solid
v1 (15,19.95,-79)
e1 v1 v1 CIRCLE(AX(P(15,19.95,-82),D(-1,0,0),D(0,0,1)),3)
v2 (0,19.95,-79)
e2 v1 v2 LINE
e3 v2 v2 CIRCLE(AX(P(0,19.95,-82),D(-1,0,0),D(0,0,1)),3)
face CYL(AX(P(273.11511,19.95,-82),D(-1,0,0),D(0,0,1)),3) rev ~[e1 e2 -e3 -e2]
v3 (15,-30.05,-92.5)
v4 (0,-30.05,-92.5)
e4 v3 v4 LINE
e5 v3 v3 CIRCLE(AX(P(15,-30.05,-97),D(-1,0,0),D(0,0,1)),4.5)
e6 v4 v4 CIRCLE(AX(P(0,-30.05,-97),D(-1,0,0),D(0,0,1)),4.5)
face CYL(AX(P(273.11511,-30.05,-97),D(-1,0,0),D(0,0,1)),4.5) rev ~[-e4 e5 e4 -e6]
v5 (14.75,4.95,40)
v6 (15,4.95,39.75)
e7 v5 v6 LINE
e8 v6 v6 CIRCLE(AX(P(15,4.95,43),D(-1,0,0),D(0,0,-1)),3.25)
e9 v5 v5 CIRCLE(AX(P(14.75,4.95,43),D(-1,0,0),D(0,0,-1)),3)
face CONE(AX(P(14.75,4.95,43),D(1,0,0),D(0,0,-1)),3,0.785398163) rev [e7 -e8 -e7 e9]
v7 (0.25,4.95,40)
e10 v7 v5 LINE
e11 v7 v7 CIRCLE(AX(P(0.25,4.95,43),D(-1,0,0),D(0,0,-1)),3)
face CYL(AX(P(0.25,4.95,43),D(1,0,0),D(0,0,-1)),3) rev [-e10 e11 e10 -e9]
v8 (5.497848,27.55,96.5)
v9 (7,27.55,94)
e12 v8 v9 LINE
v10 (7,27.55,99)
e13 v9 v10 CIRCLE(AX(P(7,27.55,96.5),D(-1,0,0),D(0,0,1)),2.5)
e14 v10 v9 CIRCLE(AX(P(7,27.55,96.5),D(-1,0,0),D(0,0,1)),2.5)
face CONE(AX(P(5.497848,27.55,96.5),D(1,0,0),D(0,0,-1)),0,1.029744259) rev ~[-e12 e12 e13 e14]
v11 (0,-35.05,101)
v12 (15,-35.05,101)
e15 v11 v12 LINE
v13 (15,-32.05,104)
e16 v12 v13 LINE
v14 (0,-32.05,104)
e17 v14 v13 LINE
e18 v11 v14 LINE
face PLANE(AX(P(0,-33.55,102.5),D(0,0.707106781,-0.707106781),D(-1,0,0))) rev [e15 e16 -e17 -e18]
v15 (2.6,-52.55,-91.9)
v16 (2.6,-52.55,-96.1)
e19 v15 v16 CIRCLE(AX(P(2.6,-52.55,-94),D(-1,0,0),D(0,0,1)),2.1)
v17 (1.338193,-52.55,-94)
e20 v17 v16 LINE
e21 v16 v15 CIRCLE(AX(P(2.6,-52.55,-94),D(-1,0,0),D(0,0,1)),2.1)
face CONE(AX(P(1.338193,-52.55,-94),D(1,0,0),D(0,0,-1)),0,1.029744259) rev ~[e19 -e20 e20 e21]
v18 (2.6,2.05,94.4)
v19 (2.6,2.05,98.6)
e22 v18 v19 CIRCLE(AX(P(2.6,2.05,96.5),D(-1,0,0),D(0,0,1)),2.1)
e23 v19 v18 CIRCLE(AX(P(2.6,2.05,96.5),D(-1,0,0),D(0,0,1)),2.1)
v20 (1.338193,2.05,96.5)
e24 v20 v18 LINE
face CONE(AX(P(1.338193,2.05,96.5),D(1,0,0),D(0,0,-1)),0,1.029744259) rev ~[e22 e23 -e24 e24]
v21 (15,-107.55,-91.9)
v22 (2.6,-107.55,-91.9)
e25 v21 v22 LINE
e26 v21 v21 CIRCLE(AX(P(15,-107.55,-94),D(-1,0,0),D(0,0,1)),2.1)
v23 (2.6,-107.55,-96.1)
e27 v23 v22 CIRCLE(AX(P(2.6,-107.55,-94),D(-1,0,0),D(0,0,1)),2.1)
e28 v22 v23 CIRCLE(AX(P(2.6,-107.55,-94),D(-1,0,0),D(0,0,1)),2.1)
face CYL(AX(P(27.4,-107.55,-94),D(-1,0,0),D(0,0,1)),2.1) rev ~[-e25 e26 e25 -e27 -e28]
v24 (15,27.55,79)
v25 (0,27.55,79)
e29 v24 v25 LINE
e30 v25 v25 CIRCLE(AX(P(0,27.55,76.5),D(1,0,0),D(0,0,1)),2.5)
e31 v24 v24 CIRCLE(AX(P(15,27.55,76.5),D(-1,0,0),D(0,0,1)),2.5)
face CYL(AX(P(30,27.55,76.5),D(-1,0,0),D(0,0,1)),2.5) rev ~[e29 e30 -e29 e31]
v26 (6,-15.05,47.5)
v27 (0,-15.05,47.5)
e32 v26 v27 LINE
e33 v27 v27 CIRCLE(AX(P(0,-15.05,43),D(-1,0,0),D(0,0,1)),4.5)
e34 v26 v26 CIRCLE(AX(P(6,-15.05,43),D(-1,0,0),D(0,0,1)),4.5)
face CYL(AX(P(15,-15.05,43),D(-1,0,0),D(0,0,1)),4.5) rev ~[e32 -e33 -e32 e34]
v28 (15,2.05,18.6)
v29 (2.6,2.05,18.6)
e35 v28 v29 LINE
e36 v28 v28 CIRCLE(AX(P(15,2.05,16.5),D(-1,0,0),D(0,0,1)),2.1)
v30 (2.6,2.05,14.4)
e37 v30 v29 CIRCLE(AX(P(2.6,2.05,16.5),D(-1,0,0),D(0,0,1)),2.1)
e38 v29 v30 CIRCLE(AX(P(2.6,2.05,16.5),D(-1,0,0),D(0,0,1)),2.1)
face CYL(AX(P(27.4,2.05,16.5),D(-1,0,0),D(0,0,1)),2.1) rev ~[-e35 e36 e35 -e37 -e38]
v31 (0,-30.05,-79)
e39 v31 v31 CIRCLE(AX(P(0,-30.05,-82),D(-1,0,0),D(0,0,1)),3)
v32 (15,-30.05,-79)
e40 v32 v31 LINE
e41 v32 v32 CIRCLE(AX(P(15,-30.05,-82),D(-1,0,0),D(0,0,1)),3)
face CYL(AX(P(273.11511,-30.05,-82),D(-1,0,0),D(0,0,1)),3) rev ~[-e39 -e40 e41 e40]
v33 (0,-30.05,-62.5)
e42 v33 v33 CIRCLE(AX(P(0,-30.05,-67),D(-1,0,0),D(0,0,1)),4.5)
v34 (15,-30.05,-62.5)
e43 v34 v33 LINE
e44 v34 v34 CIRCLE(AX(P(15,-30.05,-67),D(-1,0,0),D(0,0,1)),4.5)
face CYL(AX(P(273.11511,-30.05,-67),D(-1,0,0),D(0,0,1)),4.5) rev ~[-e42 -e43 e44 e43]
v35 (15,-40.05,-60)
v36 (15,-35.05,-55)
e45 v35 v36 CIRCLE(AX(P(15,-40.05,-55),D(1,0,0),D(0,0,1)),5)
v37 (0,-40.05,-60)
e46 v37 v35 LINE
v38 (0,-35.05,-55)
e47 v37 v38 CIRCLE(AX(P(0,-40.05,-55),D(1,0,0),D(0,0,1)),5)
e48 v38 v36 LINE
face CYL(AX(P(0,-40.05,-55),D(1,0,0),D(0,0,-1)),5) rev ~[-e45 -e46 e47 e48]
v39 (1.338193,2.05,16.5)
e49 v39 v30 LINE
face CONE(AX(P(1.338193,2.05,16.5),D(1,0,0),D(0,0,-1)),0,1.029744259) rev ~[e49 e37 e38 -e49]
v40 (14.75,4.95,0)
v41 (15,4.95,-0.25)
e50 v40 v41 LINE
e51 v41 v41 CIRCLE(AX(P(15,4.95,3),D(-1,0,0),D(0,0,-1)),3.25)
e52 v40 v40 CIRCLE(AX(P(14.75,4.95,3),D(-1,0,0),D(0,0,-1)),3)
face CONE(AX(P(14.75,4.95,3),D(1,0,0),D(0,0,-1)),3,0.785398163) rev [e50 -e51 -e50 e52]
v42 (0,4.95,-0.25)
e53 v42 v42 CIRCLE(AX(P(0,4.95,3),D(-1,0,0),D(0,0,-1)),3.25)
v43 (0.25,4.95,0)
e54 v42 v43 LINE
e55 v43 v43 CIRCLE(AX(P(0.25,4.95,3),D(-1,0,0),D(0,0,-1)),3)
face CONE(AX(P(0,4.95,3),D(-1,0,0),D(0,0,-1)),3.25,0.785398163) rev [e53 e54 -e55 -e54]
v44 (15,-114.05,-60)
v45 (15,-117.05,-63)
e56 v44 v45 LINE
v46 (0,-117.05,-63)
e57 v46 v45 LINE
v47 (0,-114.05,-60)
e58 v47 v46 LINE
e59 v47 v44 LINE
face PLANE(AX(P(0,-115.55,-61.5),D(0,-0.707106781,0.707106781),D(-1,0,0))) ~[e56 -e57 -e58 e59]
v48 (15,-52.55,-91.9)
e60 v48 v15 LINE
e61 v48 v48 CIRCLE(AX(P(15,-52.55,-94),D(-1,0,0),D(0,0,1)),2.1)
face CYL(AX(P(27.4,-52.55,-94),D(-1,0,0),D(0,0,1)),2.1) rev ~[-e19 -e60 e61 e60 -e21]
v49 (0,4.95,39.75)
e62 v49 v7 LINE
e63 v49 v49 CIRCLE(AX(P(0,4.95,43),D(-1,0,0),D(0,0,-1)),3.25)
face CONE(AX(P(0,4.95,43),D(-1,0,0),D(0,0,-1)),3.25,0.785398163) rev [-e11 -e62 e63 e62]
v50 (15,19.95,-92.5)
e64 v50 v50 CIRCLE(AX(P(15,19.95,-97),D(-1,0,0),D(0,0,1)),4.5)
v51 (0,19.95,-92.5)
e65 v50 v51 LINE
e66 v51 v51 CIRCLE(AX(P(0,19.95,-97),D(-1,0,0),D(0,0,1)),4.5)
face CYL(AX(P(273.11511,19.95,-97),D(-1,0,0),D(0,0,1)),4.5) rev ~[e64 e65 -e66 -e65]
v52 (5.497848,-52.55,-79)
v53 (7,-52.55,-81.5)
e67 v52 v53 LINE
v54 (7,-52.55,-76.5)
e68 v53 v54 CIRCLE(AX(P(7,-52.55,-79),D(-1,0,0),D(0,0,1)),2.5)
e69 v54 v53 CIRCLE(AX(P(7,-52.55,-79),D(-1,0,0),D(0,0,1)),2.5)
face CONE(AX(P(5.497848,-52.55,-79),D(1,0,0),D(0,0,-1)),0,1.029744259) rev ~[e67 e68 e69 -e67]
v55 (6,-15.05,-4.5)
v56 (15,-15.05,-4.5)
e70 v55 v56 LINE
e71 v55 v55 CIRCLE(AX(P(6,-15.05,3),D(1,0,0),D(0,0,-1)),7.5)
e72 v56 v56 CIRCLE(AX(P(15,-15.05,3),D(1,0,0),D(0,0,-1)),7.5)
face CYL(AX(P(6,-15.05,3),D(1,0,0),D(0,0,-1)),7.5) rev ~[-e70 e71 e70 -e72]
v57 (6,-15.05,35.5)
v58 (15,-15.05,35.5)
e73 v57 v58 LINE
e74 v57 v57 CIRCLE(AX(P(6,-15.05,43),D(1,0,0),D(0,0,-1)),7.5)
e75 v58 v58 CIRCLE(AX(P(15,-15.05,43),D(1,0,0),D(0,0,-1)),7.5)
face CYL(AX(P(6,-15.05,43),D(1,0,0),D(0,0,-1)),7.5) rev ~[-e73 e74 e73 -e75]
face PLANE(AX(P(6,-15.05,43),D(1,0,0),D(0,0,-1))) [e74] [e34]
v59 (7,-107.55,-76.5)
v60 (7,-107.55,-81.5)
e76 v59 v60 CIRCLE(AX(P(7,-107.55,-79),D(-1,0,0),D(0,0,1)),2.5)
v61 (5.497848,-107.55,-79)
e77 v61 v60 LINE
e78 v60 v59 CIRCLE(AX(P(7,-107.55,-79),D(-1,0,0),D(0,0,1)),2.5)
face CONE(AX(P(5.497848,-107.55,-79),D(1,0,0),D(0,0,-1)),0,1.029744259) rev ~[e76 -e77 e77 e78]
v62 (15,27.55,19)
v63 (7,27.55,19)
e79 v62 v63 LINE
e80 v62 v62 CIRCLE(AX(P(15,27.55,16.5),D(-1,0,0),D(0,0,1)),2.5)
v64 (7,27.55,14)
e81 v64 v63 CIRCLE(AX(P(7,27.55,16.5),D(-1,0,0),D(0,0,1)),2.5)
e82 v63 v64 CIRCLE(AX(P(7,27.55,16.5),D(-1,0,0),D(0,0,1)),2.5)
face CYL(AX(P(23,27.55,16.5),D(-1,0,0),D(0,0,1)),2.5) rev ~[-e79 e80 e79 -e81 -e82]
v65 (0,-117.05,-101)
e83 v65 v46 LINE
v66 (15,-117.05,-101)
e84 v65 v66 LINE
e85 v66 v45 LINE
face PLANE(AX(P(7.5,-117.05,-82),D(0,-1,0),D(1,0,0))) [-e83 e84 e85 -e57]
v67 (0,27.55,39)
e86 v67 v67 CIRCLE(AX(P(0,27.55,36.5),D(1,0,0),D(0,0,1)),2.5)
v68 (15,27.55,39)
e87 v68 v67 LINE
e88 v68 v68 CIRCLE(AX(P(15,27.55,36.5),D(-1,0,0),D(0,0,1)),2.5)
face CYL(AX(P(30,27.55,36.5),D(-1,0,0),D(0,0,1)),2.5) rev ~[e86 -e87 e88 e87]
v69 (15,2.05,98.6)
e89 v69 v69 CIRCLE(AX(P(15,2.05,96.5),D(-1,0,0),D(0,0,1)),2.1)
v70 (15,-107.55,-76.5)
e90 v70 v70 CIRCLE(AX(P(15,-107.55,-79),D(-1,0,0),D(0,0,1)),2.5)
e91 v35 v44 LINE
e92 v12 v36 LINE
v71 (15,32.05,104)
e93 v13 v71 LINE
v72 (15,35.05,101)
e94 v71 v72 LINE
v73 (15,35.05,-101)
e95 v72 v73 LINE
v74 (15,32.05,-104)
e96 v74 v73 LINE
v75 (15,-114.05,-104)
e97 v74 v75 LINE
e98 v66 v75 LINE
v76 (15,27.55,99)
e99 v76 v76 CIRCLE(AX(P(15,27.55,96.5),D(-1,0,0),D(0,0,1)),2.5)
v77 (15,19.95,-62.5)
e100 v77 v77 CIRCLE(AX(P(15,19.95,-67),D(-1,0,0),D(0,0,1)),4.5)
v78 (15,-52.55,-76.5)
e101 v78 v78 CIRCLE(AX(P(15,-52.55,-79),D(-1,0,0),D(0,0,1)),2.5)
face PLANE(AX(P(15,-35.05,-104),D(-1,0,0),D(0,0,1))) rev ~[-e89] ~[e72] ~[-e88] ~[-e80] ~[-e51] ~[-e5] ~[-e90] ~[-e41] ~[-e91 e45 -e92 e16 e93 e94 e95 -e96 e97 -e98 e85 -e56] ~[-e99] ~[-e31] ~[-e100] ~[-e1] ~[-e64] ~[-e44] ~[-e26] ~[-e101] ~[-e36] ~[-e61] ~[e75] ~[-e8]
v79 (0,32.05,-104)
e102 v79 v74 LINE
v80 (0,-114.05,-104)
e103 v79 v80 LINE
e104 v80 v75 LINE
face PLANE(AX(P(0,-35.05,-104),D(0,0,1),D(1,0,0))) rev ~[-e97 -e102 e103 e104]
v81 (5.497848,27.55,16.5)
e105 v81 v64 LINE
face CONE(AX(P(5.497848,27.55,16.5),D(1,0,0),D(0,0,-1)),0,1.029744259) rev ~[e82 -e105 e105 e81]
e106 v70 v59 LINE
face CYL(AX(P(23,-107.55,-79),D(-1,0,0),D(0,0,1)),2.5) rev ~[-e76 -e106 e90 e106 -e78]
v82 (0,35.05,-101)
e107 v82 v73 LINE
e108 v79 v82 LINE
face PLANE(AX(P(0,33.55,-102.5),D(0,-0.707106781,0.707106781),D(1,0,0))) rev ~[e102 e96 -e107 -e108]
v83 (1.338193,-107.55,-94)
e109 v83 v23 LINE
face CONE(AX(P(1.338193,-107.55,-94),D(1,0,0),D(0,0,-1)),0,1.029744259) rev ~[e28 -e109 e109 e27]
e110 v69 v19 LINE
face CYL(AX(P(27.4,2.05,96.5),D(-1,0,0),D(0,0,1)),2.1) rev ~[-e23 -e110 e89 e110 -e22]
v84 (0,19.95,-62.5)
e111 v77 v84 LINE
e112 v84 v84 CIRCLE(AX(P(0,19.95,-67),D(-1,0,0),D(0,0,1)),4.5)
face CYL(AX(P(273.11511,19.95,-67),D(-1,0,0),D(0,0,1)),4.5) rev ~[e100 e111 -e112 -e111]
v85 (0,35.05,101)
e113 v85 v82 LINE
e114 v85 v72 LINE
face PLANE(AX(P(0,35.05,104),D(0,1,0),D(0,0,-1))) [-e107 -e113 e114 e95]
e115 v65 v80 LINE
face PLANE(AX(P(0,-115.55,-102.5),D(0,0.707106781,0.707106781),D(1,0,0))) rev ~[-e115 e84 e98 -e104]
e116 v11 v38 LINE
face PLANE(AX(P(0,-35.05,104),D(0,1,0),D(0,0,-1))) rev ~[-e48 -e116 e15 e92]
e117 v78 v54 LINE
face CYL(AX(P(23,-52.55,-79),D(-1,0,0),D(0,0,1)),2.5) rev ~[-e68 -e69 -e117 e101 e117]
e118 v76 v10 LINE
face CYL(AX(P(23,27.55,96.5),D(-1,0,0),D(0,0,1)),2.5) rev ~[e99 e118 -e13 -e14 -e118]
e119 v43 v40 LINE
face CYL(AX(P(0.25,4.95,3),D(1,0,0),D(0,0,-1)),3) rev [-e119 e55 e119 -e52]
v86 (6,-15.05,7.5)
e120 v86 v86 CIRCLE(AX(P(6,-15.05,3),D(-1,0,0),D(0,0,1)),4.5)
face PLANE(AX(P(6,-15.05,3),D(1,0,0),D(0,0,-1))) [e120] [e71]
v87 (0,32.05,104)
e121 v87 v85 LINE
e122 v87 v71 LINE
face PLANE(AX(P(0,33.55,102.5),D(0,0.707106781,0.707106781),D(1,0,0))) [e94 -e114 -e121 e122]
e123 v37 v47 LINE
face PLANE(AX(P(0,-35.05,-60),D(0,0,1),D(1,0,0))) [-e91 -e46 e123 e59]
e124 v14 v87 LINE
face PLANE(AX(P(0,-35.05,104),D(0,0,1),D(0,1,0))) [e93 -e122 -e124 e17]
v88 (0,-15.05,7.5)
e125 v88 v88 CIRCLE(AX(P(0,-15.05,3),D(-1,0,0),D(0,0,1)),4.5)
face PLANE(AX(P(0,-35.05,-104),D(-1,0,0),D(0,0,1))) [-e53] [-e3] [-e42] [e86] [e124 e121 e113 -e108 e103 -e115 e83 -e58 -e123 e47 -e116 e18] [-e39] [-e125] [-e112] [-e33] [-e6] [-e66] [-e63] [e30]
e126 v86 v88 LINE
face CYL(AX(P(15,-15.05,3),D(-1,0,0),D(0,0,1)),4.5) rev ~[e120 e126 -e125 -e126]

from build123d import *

# Parameters (mm, degrees)
SKETCH1_W                                            = 208
SKETCH1_H                                            = 70.1
BOSS_EXTRUDE1_DEPTH                                  = 15
CBORE_FOR_M8_HEXAGON_SOCKET_HEAD_CAP_SCR_D           = 9
CBORE_FOR_M8_HEXAGON_SOCKET_HEAD_CAP_SCR_CBORE_D     = 15
CBORE_FOR_M8_HEXAGON_SOCKET_HEAD_CAP_SCR_CBORE_DEPTH = 9
F_6_0MM_BLIND_HOLE_1_AT_2_COUNT                      = 2
F_6_0MM_BLIND_HOLE_1_AT_2_PITCH                      = 40
SKETCH6_W                                            = 15
SKETCH6_H                                            = 44
BOSS_EXTRUDE2_DEPTH                                  = 82
M5_TAPPED_HOLE1_D                                    = 4.2
M5_TAPPED_HOLE1_DEPTH                                = 12.4
M5_TAPPED_HOLE1_TIP                                  = 1.2618073
F_5_0MM_BLIND_HOLE_1_D                               = 5
F_5_0MM_BLIND_HOLE_1_DEPTH                           = 8
F_5_0MM_BLIND_HOLE_1_TIP                             = 1.502151548
M6_TAPPED_HOLE1_D                                    = 5
M6_TAPPED_HOLE1_DEPTH                                = 15
M6_TAPPED_HOLE1_TIP                                  = 1.502151548
F_5_0MM_BLIND_HOLE_2_D                               = 5
F_5_0MM_BLIND_HOLE_2_DEPTH                           = 8
F_5_0MM_BLIND_HOLE_2_TIP                             = 1.502151548
M5_TAPPED_HOLE2_D                                    = 4.2
M5_TAPPED_HOLE2_DEPTH                                = 12.4
M5_TAPPED_HOLE2_TIP                                  = 1.2618073
M8_CLEARANCE_HOLE1_D                                 = 9
F_6_0MM_BLIND_HOLE_2_D                               = 6
FILLET1_R                                            = 5
CHAMFER1_SIZE                                        = 3


with BuildPart() as part:
    # Sketch1 → Boss-Extrude1 (new body)
    with BuildSketch(Plane(origin=(0, 0, 0), x_dir=(0, 0, -1), z_dir=(1, 0, 0))):
        Rectangle(SKETCH1_W, SKETCH1_H)
    extrude(amount=BOSS_EXTRUDE1_DEPTH)

    # CBORE for M8 Hexagon socket head cap screws1 (through all)
    with Locations(Plane(origin=(15, 0, 0), x_dir=(0, 0, -1), z_dir=(1, 0, 0))):
        with Locations((-43, -15.05), (-3, -15.05)):
            CounterBoreHole(CBORE_FOR_M8_HEXAGON_SOCKET_HEAD_CAP_SCR_D / 2, CBORE_FOR_M8_HEXAGON_SOCKET_HEAD_CAP_SCR_CBORE_D / 2, CBORE_FOR_M8_HEXAGON_SOCKET_HEAD_CAP_SCR_CBORE_DEPTH)

    # Sketch5 → Ø6.0mm blind hole 1 (revolve, cut)
    with BuildSketch(Plane(origin=(15, 4.95, 43), x_dir=(0, 0, -1), z_dir=(0, 1, 0))):
        Polygon((0, 0), (0, 15), (3.25, 15), (3, 14.75), (3, 0.25), (3.25, 0), align=None)
    f_6_0mm_blind_hole_1 = revolve(axis=Axis((21.35, 4.95, 43), (-1, 0, 0)), mode=Mode.SUBTRACT)

    # Ø6.0mm blind hole 1 at 2: Ø6.0mm blind hole 1 ×2
    with Locations(*[(0, 0, -i * F_6_0MM_BLIND_HOLE_1_AT_2_PITCH) for i in range(1, F_6_0MM_BLIND_HOLE_1_AT_2_COUNT)]):
        add(f_6_0mm_blind_hole_1, mode=Mode.SUBTRACT)

    # Sketch6 → Boss-Extrude2 (add)
    with BuildSketch(Plane.XZ.offset(35.05)):
        with Locations((7.5, -82)):
            Rectangle(SKETCH6_W, SKETCH6_H)
    extrude(amount=BOSS_EXTRUDE2_DEPTH)

    # M5 Tapped Hole1
    with Locations(Plane(origin=(15, 0, 0), x_dir=(0, 0, -1), z_dir=(1, 0, 0))):
        with Locations((94, -107.55), (94, -52.55)):
            Hole(M5_TAPPED_HOLE1_D / 2, depth=M5_TAPPED_HOLE1_DEPTH)
            with Locations((0, 0, -(M5_TAPPED_HOLE1_DEPTH + M5_TAPPED_HOLE1_TIP / 2))):  # 118° drill point
                Cone(0, M5_TAPPED_HOLE1_D / 2, M5_TAPPED_HOLE1_TIP, mode=Mode.SUBTRACT)

    # Ø5.0mm blind hole 1
    with Locations(Plane(origin=(15, 0, 0), x_dir=(0, 0, -1), z_dir=(1, 0, 0))):
        with Locations((79, -52.55), (79, -107.55)):
            Hole(F_5_0MM_BLIND_HOLE_1_D / 2, depth=F_5_0MM_BLIND_HOLE_1_DEPTH)
            with Locations((0, 0, -(F_5_0MM_BLIND_HOLE_1_DEPTH + F_5_0MM_BLIND_HOLE_1_TIP / 2))):  # 118° drill point
                Cone(0, F_5_0MM_BLIND_HOLE_1_D / 2, F_5_0MM_BLIND_HOLE_1_TIP, mode=Mode.SUBTRACT)

    # M6 Tapped Hole1
    with Locations(Plane(origin=(15, 0, 0), x_dir=(0, 0, -1), z_dir=(1, 0, 0))):
        with Locations((-76.5, 27.55), (-36.5, 27.55)):
            Hole(M6_TAPPED_HOLE1_D / 2, depth=M6_TAPPED_HOLE1_DEPTH)
            with Locations((0, 0, -(M6_TAPPED_HOLE1_DEPTH + M6_TAPPED_HOLE1_TIP / 2))):  # 118° drill point
                Cone(0, M6_TAPPED_HOLE1_D / 2, M6_TAPPED_HOLE1_TIP, mode=Mode.SUBTRACT)

    # Ø5.0mm blind hole 2
    with Locations(Plane(origin=(15, 0, 0), x_dir=(0, 0, -1), z_dir=(1, 0, 0))):
        with Locations((-96.5, 27.55), (-16.5, 27.55)):
            Hole(F_5_0MM_BLIND_HOLE_2_D / 2, depth=F_5_0MM_BLIND_HOLE_2_DEPTH)
            with Locations((0, 0, -(F_5_0MM_BLIND_HOLE_2_DEPTH + F_5_0MM_BLIND_HOLE_2_TIP / 2))):  # 118° drill point
                Cone(0, F_5_0MM_BLIND_HOLE_2_D / 2, F_5_0MM_BLIND_HOLE_2_TIP, mode=Mode.SUBTRACT)

    # M5 Tapped Hole2
    with Locations(Plane(origin=(15, 0, 0), x_dir=(0, 0, -1), z_dir=(1, 0, 0))):
        with Locations((-96.5, 2.05), (-16.5, 2.05)):
            Hole(M5_TAPPED_HOLE2_D / 2, depth=M5_TAPPED_HOLE2_DEPTH)
            with Locations((0, 0, -(M5_TAPPED_HOLE2_DEPTH + M5_TAPPED_HOLE2_TIP / 2))):  # 118° drill point
                Cone(0, M5_TAPPED_HOLE2_D / 2, M5_TAPPED_HOLE2_TIP, mode=Mode.SUBTRACT)

    # M8 Clearance Hole1 (through all)
    with Locations(Plane(origin=(15, 0, 0), x_dir=(0, 0, -1), z_dir=(1, 0, 0))):
        with Locations((67, -30.05), (97, -30.05), (67, 19.95), (97, 19.95)):
            Hole(M8_CLEARANCE_HOLE1_D / 2)

    # Ø6.0mm blind hole 2 (through all)
    with Locations(Plane(origin=(15, 0, 0), x_dir=(0, 0, -1), z_dir=(1, 0, 0))):
        with Locations((82, -30.05), (82, 19.95)):
            Hole(F_6_0MM_BLIND_HOLE_2_D / 2)

    # Fillet1
    fillet1_edges = [part.edges().sort_by_distance(p)[0] for p in [
        (7.5, -35.05, -60),
    ]]
    fillet(fillet1_edges, radius=FILLET1_R)

    # Chamfer1
    chamfer1_edges = [part.edges().sort_by_distance(p)[0] for p in [
        (7.5, -117.05, -104),
        (7.5, -117.05, -60),
        (7.5, -35.05, 104),
        (7.5, 35.05, 104),
        (7.5, 35.05, -104),
    ]]
    chamfer(chamfer1_edges, length=CHAMFER1_SIZE)


solid = part.part
